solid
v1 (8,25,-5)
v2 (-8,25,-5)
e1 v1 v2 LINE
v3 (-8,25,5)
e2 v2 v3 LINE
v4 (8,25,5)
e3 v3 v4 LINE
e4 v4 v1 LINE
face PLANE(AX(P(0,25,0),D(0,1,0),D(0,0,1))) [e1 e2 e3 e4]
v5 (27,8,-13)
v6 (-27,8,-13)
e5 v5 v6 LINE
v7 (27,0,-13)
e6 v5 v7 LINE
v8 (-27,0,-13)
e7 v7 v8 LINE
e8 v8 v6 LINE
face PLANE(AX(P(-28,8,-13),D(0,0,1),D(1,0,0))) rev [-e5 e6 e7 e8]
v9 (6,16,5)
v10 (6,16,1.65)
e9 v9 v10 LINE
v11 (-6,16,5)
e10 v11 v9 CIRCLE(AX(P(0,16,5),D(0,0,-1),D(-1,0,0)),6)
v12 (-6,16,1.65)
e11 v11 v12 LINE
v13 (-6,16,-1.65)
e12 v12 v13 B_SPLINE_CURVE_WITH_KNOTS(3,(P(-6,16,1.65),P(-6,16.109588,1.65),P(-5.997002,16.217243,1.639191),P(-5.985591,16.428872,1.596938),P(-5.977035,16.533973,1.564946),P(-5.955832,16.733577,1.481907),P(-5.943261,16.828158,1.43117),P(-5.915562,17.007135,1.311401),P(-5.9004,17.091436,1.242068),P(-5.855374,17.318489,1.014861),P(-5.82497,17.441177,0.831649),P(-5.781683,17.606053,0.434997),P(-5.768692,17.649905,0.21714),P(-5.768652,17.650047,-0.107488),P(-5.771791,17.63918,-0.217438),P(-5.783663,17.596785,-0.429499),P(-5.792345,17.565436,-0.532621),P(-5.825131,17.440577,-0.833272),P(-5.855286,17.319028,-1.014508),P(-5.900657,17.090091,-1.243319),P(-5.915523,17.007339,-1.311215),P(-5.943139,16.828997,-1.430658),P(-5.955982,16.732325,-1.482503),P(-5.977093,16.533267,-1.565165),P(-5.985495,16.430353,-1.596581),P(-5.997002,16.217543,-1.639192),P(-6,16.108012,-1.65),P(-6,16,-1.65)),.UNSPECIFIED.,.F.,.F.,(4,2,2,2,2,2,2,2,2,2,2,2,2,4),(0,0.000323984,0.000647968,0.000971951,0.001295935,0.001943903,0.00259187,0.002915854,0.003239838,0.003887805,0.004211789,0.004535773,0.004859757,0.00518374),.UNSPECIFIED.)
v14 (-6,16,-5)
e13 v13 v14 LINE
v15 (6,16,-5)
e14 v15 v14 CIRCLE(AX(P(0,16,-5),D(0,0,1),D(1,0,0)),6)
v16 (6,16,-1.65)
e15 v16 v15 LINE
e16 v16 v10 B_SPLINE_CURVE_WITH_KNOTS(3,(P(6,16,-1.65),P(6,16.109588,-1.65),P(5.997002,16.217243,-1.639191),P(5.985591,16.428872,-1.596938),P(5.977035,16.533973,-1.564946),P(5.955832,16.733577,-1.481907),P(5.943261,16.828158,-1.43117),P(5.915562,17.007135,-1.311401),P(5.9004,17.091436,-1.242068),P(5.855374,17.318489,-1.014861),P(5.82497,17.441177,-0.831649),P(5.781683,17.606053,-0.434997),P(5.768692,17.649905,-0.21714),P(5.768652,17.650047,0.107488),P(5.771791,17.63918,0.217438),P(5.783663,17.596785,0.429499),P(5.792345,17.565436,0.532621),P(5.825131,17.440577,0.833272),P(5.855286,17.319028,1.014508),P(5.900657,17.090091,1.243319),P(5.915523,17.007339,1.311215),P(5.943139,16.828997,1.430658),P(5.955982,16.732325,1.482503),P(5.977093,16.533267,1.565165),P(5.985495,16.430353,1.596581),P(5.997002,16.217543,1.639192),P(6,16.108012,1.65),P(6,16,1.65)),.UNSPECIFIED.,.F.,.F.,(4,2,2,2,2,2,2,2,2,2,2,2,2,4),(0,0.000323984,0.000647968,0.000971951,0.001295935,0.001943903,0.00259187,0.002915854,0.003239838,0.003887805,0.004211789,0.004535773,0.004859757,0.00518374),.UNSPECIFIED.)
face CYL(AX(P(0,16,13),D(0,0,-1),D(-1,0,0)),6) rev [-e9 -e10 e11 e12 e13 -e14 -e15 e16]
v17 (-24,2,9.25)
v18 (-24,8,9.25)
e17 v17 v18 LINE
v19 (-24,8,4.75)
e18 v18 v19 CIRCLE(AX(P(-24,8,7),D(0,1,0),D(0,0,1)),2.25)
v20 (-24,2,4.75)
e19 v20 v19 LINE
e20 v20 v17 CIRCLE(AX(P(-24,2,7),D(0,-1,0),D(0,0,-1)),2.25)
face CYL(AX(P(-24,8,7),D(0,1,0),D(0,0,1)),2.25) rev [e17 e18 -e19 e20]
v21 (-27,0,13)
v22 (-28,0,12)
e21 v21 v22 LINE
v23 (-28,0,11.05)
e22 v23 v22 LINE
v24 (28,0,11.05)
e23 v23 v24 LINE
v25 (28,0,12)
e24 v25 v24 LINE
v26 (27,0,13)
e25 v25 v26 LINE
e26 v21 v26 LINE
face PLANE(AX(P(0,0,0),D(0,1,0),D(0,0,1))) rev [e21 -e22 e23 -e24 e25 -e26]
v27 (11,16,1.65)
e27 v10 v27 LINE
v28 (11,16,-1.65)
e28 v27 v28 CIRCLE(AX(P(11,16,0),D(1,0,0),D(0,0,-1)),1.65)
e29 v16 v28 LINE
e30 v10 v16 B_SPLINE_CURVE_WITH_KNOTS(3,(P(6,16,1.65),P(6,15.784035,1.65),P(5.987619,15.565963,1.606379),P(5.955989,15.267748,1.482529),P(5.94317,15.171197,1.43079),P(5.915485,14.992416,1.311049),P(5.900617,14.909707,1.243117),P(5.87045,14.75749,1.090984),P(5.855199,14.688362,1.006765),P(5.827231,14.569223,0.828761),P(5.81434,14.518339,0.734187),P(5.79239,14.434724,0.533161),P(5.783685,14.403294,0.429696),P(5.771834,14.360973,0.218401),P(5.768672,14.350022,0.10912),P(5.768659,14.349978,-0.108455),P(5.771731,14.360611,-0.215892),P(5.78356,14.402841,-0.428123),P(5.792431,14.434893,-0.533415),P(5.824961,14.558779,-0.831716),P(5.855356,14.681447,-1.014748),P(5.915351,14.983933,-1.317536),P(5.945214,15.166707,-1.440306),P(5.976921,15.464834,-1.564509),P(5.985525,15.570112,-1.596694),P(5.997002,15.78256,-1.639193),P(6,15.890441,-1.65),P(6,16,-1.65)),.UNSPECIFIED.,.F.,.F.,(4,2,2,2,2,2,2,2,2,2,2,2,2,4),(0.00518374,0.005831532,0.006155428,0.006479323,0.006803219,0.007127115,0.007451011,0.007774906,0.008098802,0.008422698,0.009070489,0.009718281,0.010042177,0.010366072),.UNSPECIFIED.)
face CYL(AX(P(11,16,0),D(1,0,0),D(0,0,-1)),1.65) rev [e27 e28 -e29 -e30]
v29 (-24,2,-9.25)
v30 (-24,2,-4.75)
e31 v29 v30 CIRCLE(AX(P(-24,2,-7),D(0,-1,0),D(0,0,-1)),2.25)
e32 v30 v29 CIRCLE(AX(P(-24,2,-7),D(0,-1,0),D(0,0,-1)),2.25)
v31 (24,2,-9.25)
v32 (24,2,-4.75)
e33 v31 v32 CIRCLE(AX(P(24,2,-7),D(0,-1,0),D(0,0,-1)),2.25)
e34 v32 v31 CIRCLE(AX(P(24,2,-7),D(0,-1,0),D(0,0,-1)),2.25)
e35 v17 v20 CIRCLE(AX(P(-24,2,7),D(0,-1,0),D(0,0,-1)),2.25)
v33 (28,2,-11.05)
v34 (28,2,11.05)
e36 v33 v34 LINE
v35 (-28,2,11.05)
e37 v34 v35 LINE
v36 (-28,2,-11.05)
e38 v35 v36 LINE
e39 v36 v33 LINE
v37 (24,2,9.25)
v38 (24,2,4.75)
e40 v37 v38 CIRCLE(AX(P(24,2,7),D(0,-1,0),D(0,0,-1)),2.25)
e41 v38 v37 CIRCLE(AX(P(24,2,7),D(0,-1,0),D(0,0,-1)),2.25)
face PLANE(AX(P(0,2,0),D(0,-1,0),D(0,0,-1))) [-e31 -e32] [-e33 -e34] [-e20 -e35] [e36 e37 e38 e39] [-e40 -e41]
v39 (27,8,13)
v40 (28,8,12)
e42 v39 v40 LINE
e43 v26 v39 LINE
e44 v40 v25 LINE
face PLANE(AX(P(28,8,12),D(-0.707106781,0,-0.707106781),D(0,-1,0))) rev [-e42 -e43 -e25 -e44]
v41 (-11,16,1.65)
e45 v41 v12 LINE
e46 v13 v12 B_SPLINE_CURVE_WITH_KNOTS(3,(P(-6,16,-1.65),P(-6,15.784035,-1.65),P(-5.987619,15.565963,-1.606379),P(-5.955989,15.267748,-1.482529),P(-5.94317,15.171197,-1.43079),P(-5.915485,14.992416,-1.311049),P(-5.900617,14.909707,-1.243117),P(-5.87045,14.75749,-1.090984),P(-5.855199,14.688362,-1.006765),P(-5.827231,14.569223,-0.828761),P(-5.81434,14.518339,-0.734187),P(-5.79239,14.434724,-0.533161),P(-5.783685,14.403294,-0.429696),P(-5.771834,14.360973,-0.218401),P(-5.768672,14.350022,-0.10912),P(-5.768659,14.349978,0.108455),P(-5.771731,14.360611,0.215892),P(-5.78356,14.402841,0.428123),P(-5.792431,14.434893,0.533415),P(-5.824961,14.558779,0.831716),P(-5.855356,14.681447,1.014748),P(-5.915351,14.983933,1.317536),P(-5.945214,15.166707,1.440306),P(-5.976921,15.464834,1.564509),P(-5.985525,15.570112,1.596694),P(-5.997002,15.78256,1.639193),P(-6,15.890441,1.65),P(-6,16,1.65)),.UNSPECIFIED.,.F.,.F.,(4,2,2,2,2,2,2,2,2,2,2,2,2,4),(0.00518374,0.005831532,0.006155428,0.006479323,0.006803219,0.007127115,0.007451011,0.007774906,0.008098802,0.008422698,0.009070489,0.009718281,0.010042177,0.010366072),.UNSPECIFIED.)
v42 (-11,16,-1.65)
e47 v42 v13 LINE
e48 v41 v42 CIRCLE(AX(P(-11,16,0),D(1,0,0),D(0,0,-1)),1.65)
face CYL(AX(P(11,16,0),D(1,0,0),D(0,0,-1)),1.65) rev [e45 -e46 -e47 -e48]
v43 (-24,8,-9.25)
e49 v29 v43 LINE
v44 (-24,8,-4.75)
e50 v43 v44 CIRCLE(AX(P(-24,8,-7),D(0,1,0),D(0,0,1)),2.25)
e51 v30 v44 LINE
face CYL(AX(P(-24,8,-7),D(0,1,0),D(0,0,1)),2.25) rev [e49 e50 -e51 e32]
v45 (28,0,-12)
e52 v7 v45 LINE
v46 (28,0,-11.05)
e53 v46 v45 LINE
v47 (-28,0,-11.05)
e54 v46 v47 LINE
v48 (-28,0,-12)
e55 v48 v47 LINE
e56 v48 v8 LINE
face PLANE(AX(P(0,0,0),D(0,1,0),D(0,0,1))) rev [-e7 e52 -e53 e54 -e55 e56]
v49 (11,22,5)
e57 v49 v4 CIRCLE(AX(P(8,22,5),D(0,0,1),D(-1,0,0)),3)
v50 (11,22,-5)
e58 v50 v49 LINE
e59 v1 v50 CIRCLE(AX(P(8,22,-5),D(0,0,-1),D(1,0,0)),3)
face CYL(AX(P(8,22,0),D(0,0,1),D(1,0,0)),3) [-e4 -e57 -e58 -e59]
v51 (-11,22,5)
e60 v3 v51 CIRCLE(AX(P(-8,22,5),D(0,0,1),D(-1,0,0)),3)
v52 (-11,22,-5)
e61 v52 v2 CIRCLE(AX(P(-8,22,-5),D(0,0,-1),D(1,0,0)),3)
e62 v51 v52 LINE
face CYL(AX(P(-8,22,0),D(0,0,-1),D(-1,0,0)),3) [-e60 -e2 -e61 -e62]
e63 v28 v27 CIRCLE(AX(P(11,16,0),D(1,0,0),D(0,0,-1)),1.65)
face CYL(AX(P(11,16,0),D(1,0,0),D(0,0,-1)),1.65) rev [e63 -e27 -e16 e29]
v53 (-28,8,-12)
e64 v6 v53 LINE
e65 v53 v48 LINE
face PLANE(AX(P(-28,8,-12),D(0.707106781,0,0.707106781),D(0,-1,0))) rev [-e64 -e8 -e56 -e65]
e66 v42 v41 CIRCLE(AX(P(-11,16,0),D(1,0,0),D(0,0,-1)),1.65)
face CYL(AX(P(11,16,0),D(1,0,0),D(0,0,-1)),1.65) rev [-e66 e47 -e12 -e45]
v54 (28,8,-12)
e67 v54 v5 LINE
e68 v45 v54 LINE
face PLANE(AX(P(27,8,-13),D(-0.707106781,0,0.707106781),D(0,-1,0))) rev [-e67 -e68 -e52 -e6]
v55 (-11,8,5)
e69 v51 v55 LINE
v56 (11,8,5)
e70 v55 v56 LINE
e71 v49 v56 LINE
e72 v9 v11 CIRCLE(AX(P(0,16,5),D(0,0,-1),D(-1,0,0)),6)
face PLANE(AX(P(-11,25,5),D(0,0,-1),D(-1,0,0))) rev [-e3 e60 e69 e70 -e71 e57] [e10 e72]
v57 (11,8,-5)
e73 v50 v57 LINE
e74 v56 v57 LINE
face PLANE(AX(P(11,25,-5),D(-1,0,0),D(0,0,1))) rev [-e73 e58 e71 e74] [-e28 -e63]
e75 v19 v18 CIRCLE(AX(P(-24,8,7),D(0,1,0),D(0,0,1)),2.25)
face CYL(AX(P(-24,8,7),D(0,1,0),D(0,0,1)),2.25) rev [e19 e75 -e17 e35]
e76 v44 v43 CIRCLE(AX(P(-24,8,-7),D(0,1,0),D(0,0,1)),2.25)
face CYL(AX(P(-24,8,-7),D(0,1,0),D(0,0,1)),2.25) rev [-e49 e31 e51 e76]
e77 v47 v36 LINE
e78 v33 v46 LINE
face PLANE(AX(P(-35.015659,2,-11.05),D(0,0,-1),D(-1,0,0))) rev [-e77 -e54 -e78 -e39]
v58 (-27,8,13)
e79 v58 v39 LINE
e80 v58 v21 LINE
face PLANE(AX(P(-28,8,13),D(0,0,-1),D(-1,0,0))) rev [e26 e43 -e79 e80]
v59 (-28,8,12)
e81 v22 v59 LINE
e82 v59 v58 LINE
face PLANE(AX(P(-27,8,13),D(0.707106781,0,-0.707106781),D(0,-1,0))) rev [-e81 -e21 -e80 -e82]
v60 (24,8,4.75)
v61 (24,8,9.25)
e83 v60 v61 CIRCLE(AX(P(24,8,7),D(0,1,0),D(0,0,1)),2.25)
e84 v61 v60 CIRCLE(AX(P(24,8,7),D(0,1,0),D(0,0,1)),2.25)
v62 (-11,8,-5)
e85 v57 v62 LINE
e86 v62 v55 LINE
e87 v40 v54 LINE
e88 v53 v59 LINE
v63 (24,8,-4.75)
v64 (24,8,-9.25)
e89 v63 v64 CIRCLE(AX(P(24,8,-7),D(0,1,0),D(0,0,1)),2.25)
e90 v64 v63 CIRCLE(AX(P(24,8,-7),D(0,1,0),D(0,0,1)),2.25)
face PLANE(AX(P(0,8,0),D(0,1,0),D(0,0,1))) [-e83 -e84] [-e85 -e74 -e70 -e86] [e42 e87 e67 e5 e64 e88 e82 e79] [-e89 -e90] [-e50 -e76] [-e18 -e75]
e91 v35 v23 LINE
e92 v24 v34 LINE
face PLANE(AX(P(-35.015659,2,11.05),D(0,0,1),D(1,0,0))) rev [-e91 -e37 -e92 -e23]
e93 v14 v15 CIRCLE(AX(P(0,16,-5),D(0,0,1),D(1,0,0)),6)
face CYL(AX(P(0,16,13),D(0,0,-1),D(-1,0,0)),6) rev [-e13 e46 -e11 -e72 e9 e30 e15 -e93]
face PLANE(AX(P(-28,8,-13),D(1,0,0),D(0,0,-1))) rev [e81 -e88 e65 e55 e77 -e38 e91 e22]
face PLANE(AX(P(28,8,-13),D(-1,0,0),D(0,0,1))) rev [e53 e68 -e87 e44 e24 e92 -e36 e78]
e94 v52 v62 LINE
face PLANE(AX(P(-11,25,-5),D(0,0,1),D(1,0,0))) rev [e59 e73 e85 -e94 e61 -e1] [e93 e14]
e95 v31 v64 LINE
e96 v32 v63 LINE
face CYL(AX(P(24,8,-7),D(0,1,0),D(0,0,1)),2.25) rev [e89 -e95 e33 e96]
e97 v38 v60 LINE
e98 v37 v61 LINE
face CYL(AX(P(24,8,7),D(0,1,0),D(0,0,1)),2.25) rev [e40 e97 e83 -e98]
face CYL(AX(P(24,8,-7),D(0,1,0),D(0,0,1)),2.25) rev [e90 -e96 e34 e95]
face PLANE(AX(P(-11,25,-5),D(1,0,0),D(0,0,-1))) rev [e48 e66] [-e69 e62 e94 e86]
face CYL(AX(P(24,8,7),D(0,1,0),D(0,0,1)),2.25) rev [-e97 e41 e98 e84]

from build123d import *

# Parameters (mm, degrees)
SKETCH_1_W              = 56
SKETCH_1_H              = 26
EXTRUDE_1_DEPTH         = 8
SKETCH_2_W              = 70.031318806
SKETCH_2_H              = 22.1
CUT_EXTRUDE_1_DEPTH     = 2
SKETCH_3_W              = 22
SKETCH_3_H              = 10
EXTRUDE_2_DEPTH         = 17
SKETCH_4_R              = 6
CUT_EXTRUDE_2_DEPTH     = 46.661800227
HOLE_WIZARD_4_5_4_5_1_D = 4.5
FILLET_2_R              = 3
HOLE_WIZARD_M4_1_D      = 3.3
CHAMFER_1_SIZE          = 1


with BuildPart() as part:
    # 草图1 → 凸台-拉伸1 (new body)
    with BuildSketch(Plane(origin=(0, 0, 0), x_dir=(1, 0, 0), z_dir=(0, 1, 0))):
        Rectangle(SKETCH_1_W, SKETCH_1_H)
    extrude(amount=EXTRUDE_1_DEPTH)

    # 草图2 → 切除-拉伸1 (cut)
    with BuildSketch(Plane.XZ):
        Rectangle(SKETCH_2_W, SKETCH_2_H)
    extrude(amount=-CUT_EXTRUDE_1_DEPTH, mode=Mode.SUBTRACT)

    # 草图3 → 凸台-拉伸2 (add)
    with BuildSketch(Plane(origin=(0, 8, 0), x_dir=(1, 0, 0), z_dir=(0, 1, 0))):
        Rectangle(SKETCH_3_W, SKETCH_3_H)
    extrude(amount=EXTRUDE_2_DEPTH)

    # 草图4 → 切除-拉伸2 (cut, through all)
    with BuildSketch(Plane(origin=(0, 0, -13), x_dir=(-1, 0, 0), z_dir=(0, 0, -1))):
        with Locations((0, 16)):
            Circle(SKETCH_4_R)
    extrude(amount=-CUT_EXTRUDE_2_DEPTH, mode=Mode.SUBTRACT)

    # Ø4.5 (4.5) 直径孔1 (through all)
    with Locations(Plane(origin=(0, 8, 0), x_dir=(1, 0, 0), z_dir=(0, 1, 0))):
        with Locations((-24, 7), (-24, -7), (24, 7), (24, -7)):
            Hole(HOLE_WIZARD_4_5_4_5_1_D / 2)

    # 圆角2
    fillet_2_edges = [part.edges().sort_by_distance(p)[0] for p in [
        (11, 25, 0),
        (-11, 25, 0),
    ]]
    fillet(fillet_2_edges, radius=FILLET_2_R)

    # M4 螺纹孔1 (through all)
    with Locations(Plane(origin=(11, 0, 0), x_dir=(0, 0, -1), z_dir=(1, 0, 0))):
        with Locations((0, 16)):
            Hole(HOLE_WIZARD_M4_1_D / 2)

    # 倒角1
    chamfer_1_edges = [part.edges().sort_by_distance(p)[0] for p in [
        (28, 4, 13),
        (-28, 4, 13),
        (-28, 4, -13),
        (28, 4, -13),
    ]]
    chamfer(chamfer_1_edges, length=CHAMFER_1_SIZE)


solid = part.part
